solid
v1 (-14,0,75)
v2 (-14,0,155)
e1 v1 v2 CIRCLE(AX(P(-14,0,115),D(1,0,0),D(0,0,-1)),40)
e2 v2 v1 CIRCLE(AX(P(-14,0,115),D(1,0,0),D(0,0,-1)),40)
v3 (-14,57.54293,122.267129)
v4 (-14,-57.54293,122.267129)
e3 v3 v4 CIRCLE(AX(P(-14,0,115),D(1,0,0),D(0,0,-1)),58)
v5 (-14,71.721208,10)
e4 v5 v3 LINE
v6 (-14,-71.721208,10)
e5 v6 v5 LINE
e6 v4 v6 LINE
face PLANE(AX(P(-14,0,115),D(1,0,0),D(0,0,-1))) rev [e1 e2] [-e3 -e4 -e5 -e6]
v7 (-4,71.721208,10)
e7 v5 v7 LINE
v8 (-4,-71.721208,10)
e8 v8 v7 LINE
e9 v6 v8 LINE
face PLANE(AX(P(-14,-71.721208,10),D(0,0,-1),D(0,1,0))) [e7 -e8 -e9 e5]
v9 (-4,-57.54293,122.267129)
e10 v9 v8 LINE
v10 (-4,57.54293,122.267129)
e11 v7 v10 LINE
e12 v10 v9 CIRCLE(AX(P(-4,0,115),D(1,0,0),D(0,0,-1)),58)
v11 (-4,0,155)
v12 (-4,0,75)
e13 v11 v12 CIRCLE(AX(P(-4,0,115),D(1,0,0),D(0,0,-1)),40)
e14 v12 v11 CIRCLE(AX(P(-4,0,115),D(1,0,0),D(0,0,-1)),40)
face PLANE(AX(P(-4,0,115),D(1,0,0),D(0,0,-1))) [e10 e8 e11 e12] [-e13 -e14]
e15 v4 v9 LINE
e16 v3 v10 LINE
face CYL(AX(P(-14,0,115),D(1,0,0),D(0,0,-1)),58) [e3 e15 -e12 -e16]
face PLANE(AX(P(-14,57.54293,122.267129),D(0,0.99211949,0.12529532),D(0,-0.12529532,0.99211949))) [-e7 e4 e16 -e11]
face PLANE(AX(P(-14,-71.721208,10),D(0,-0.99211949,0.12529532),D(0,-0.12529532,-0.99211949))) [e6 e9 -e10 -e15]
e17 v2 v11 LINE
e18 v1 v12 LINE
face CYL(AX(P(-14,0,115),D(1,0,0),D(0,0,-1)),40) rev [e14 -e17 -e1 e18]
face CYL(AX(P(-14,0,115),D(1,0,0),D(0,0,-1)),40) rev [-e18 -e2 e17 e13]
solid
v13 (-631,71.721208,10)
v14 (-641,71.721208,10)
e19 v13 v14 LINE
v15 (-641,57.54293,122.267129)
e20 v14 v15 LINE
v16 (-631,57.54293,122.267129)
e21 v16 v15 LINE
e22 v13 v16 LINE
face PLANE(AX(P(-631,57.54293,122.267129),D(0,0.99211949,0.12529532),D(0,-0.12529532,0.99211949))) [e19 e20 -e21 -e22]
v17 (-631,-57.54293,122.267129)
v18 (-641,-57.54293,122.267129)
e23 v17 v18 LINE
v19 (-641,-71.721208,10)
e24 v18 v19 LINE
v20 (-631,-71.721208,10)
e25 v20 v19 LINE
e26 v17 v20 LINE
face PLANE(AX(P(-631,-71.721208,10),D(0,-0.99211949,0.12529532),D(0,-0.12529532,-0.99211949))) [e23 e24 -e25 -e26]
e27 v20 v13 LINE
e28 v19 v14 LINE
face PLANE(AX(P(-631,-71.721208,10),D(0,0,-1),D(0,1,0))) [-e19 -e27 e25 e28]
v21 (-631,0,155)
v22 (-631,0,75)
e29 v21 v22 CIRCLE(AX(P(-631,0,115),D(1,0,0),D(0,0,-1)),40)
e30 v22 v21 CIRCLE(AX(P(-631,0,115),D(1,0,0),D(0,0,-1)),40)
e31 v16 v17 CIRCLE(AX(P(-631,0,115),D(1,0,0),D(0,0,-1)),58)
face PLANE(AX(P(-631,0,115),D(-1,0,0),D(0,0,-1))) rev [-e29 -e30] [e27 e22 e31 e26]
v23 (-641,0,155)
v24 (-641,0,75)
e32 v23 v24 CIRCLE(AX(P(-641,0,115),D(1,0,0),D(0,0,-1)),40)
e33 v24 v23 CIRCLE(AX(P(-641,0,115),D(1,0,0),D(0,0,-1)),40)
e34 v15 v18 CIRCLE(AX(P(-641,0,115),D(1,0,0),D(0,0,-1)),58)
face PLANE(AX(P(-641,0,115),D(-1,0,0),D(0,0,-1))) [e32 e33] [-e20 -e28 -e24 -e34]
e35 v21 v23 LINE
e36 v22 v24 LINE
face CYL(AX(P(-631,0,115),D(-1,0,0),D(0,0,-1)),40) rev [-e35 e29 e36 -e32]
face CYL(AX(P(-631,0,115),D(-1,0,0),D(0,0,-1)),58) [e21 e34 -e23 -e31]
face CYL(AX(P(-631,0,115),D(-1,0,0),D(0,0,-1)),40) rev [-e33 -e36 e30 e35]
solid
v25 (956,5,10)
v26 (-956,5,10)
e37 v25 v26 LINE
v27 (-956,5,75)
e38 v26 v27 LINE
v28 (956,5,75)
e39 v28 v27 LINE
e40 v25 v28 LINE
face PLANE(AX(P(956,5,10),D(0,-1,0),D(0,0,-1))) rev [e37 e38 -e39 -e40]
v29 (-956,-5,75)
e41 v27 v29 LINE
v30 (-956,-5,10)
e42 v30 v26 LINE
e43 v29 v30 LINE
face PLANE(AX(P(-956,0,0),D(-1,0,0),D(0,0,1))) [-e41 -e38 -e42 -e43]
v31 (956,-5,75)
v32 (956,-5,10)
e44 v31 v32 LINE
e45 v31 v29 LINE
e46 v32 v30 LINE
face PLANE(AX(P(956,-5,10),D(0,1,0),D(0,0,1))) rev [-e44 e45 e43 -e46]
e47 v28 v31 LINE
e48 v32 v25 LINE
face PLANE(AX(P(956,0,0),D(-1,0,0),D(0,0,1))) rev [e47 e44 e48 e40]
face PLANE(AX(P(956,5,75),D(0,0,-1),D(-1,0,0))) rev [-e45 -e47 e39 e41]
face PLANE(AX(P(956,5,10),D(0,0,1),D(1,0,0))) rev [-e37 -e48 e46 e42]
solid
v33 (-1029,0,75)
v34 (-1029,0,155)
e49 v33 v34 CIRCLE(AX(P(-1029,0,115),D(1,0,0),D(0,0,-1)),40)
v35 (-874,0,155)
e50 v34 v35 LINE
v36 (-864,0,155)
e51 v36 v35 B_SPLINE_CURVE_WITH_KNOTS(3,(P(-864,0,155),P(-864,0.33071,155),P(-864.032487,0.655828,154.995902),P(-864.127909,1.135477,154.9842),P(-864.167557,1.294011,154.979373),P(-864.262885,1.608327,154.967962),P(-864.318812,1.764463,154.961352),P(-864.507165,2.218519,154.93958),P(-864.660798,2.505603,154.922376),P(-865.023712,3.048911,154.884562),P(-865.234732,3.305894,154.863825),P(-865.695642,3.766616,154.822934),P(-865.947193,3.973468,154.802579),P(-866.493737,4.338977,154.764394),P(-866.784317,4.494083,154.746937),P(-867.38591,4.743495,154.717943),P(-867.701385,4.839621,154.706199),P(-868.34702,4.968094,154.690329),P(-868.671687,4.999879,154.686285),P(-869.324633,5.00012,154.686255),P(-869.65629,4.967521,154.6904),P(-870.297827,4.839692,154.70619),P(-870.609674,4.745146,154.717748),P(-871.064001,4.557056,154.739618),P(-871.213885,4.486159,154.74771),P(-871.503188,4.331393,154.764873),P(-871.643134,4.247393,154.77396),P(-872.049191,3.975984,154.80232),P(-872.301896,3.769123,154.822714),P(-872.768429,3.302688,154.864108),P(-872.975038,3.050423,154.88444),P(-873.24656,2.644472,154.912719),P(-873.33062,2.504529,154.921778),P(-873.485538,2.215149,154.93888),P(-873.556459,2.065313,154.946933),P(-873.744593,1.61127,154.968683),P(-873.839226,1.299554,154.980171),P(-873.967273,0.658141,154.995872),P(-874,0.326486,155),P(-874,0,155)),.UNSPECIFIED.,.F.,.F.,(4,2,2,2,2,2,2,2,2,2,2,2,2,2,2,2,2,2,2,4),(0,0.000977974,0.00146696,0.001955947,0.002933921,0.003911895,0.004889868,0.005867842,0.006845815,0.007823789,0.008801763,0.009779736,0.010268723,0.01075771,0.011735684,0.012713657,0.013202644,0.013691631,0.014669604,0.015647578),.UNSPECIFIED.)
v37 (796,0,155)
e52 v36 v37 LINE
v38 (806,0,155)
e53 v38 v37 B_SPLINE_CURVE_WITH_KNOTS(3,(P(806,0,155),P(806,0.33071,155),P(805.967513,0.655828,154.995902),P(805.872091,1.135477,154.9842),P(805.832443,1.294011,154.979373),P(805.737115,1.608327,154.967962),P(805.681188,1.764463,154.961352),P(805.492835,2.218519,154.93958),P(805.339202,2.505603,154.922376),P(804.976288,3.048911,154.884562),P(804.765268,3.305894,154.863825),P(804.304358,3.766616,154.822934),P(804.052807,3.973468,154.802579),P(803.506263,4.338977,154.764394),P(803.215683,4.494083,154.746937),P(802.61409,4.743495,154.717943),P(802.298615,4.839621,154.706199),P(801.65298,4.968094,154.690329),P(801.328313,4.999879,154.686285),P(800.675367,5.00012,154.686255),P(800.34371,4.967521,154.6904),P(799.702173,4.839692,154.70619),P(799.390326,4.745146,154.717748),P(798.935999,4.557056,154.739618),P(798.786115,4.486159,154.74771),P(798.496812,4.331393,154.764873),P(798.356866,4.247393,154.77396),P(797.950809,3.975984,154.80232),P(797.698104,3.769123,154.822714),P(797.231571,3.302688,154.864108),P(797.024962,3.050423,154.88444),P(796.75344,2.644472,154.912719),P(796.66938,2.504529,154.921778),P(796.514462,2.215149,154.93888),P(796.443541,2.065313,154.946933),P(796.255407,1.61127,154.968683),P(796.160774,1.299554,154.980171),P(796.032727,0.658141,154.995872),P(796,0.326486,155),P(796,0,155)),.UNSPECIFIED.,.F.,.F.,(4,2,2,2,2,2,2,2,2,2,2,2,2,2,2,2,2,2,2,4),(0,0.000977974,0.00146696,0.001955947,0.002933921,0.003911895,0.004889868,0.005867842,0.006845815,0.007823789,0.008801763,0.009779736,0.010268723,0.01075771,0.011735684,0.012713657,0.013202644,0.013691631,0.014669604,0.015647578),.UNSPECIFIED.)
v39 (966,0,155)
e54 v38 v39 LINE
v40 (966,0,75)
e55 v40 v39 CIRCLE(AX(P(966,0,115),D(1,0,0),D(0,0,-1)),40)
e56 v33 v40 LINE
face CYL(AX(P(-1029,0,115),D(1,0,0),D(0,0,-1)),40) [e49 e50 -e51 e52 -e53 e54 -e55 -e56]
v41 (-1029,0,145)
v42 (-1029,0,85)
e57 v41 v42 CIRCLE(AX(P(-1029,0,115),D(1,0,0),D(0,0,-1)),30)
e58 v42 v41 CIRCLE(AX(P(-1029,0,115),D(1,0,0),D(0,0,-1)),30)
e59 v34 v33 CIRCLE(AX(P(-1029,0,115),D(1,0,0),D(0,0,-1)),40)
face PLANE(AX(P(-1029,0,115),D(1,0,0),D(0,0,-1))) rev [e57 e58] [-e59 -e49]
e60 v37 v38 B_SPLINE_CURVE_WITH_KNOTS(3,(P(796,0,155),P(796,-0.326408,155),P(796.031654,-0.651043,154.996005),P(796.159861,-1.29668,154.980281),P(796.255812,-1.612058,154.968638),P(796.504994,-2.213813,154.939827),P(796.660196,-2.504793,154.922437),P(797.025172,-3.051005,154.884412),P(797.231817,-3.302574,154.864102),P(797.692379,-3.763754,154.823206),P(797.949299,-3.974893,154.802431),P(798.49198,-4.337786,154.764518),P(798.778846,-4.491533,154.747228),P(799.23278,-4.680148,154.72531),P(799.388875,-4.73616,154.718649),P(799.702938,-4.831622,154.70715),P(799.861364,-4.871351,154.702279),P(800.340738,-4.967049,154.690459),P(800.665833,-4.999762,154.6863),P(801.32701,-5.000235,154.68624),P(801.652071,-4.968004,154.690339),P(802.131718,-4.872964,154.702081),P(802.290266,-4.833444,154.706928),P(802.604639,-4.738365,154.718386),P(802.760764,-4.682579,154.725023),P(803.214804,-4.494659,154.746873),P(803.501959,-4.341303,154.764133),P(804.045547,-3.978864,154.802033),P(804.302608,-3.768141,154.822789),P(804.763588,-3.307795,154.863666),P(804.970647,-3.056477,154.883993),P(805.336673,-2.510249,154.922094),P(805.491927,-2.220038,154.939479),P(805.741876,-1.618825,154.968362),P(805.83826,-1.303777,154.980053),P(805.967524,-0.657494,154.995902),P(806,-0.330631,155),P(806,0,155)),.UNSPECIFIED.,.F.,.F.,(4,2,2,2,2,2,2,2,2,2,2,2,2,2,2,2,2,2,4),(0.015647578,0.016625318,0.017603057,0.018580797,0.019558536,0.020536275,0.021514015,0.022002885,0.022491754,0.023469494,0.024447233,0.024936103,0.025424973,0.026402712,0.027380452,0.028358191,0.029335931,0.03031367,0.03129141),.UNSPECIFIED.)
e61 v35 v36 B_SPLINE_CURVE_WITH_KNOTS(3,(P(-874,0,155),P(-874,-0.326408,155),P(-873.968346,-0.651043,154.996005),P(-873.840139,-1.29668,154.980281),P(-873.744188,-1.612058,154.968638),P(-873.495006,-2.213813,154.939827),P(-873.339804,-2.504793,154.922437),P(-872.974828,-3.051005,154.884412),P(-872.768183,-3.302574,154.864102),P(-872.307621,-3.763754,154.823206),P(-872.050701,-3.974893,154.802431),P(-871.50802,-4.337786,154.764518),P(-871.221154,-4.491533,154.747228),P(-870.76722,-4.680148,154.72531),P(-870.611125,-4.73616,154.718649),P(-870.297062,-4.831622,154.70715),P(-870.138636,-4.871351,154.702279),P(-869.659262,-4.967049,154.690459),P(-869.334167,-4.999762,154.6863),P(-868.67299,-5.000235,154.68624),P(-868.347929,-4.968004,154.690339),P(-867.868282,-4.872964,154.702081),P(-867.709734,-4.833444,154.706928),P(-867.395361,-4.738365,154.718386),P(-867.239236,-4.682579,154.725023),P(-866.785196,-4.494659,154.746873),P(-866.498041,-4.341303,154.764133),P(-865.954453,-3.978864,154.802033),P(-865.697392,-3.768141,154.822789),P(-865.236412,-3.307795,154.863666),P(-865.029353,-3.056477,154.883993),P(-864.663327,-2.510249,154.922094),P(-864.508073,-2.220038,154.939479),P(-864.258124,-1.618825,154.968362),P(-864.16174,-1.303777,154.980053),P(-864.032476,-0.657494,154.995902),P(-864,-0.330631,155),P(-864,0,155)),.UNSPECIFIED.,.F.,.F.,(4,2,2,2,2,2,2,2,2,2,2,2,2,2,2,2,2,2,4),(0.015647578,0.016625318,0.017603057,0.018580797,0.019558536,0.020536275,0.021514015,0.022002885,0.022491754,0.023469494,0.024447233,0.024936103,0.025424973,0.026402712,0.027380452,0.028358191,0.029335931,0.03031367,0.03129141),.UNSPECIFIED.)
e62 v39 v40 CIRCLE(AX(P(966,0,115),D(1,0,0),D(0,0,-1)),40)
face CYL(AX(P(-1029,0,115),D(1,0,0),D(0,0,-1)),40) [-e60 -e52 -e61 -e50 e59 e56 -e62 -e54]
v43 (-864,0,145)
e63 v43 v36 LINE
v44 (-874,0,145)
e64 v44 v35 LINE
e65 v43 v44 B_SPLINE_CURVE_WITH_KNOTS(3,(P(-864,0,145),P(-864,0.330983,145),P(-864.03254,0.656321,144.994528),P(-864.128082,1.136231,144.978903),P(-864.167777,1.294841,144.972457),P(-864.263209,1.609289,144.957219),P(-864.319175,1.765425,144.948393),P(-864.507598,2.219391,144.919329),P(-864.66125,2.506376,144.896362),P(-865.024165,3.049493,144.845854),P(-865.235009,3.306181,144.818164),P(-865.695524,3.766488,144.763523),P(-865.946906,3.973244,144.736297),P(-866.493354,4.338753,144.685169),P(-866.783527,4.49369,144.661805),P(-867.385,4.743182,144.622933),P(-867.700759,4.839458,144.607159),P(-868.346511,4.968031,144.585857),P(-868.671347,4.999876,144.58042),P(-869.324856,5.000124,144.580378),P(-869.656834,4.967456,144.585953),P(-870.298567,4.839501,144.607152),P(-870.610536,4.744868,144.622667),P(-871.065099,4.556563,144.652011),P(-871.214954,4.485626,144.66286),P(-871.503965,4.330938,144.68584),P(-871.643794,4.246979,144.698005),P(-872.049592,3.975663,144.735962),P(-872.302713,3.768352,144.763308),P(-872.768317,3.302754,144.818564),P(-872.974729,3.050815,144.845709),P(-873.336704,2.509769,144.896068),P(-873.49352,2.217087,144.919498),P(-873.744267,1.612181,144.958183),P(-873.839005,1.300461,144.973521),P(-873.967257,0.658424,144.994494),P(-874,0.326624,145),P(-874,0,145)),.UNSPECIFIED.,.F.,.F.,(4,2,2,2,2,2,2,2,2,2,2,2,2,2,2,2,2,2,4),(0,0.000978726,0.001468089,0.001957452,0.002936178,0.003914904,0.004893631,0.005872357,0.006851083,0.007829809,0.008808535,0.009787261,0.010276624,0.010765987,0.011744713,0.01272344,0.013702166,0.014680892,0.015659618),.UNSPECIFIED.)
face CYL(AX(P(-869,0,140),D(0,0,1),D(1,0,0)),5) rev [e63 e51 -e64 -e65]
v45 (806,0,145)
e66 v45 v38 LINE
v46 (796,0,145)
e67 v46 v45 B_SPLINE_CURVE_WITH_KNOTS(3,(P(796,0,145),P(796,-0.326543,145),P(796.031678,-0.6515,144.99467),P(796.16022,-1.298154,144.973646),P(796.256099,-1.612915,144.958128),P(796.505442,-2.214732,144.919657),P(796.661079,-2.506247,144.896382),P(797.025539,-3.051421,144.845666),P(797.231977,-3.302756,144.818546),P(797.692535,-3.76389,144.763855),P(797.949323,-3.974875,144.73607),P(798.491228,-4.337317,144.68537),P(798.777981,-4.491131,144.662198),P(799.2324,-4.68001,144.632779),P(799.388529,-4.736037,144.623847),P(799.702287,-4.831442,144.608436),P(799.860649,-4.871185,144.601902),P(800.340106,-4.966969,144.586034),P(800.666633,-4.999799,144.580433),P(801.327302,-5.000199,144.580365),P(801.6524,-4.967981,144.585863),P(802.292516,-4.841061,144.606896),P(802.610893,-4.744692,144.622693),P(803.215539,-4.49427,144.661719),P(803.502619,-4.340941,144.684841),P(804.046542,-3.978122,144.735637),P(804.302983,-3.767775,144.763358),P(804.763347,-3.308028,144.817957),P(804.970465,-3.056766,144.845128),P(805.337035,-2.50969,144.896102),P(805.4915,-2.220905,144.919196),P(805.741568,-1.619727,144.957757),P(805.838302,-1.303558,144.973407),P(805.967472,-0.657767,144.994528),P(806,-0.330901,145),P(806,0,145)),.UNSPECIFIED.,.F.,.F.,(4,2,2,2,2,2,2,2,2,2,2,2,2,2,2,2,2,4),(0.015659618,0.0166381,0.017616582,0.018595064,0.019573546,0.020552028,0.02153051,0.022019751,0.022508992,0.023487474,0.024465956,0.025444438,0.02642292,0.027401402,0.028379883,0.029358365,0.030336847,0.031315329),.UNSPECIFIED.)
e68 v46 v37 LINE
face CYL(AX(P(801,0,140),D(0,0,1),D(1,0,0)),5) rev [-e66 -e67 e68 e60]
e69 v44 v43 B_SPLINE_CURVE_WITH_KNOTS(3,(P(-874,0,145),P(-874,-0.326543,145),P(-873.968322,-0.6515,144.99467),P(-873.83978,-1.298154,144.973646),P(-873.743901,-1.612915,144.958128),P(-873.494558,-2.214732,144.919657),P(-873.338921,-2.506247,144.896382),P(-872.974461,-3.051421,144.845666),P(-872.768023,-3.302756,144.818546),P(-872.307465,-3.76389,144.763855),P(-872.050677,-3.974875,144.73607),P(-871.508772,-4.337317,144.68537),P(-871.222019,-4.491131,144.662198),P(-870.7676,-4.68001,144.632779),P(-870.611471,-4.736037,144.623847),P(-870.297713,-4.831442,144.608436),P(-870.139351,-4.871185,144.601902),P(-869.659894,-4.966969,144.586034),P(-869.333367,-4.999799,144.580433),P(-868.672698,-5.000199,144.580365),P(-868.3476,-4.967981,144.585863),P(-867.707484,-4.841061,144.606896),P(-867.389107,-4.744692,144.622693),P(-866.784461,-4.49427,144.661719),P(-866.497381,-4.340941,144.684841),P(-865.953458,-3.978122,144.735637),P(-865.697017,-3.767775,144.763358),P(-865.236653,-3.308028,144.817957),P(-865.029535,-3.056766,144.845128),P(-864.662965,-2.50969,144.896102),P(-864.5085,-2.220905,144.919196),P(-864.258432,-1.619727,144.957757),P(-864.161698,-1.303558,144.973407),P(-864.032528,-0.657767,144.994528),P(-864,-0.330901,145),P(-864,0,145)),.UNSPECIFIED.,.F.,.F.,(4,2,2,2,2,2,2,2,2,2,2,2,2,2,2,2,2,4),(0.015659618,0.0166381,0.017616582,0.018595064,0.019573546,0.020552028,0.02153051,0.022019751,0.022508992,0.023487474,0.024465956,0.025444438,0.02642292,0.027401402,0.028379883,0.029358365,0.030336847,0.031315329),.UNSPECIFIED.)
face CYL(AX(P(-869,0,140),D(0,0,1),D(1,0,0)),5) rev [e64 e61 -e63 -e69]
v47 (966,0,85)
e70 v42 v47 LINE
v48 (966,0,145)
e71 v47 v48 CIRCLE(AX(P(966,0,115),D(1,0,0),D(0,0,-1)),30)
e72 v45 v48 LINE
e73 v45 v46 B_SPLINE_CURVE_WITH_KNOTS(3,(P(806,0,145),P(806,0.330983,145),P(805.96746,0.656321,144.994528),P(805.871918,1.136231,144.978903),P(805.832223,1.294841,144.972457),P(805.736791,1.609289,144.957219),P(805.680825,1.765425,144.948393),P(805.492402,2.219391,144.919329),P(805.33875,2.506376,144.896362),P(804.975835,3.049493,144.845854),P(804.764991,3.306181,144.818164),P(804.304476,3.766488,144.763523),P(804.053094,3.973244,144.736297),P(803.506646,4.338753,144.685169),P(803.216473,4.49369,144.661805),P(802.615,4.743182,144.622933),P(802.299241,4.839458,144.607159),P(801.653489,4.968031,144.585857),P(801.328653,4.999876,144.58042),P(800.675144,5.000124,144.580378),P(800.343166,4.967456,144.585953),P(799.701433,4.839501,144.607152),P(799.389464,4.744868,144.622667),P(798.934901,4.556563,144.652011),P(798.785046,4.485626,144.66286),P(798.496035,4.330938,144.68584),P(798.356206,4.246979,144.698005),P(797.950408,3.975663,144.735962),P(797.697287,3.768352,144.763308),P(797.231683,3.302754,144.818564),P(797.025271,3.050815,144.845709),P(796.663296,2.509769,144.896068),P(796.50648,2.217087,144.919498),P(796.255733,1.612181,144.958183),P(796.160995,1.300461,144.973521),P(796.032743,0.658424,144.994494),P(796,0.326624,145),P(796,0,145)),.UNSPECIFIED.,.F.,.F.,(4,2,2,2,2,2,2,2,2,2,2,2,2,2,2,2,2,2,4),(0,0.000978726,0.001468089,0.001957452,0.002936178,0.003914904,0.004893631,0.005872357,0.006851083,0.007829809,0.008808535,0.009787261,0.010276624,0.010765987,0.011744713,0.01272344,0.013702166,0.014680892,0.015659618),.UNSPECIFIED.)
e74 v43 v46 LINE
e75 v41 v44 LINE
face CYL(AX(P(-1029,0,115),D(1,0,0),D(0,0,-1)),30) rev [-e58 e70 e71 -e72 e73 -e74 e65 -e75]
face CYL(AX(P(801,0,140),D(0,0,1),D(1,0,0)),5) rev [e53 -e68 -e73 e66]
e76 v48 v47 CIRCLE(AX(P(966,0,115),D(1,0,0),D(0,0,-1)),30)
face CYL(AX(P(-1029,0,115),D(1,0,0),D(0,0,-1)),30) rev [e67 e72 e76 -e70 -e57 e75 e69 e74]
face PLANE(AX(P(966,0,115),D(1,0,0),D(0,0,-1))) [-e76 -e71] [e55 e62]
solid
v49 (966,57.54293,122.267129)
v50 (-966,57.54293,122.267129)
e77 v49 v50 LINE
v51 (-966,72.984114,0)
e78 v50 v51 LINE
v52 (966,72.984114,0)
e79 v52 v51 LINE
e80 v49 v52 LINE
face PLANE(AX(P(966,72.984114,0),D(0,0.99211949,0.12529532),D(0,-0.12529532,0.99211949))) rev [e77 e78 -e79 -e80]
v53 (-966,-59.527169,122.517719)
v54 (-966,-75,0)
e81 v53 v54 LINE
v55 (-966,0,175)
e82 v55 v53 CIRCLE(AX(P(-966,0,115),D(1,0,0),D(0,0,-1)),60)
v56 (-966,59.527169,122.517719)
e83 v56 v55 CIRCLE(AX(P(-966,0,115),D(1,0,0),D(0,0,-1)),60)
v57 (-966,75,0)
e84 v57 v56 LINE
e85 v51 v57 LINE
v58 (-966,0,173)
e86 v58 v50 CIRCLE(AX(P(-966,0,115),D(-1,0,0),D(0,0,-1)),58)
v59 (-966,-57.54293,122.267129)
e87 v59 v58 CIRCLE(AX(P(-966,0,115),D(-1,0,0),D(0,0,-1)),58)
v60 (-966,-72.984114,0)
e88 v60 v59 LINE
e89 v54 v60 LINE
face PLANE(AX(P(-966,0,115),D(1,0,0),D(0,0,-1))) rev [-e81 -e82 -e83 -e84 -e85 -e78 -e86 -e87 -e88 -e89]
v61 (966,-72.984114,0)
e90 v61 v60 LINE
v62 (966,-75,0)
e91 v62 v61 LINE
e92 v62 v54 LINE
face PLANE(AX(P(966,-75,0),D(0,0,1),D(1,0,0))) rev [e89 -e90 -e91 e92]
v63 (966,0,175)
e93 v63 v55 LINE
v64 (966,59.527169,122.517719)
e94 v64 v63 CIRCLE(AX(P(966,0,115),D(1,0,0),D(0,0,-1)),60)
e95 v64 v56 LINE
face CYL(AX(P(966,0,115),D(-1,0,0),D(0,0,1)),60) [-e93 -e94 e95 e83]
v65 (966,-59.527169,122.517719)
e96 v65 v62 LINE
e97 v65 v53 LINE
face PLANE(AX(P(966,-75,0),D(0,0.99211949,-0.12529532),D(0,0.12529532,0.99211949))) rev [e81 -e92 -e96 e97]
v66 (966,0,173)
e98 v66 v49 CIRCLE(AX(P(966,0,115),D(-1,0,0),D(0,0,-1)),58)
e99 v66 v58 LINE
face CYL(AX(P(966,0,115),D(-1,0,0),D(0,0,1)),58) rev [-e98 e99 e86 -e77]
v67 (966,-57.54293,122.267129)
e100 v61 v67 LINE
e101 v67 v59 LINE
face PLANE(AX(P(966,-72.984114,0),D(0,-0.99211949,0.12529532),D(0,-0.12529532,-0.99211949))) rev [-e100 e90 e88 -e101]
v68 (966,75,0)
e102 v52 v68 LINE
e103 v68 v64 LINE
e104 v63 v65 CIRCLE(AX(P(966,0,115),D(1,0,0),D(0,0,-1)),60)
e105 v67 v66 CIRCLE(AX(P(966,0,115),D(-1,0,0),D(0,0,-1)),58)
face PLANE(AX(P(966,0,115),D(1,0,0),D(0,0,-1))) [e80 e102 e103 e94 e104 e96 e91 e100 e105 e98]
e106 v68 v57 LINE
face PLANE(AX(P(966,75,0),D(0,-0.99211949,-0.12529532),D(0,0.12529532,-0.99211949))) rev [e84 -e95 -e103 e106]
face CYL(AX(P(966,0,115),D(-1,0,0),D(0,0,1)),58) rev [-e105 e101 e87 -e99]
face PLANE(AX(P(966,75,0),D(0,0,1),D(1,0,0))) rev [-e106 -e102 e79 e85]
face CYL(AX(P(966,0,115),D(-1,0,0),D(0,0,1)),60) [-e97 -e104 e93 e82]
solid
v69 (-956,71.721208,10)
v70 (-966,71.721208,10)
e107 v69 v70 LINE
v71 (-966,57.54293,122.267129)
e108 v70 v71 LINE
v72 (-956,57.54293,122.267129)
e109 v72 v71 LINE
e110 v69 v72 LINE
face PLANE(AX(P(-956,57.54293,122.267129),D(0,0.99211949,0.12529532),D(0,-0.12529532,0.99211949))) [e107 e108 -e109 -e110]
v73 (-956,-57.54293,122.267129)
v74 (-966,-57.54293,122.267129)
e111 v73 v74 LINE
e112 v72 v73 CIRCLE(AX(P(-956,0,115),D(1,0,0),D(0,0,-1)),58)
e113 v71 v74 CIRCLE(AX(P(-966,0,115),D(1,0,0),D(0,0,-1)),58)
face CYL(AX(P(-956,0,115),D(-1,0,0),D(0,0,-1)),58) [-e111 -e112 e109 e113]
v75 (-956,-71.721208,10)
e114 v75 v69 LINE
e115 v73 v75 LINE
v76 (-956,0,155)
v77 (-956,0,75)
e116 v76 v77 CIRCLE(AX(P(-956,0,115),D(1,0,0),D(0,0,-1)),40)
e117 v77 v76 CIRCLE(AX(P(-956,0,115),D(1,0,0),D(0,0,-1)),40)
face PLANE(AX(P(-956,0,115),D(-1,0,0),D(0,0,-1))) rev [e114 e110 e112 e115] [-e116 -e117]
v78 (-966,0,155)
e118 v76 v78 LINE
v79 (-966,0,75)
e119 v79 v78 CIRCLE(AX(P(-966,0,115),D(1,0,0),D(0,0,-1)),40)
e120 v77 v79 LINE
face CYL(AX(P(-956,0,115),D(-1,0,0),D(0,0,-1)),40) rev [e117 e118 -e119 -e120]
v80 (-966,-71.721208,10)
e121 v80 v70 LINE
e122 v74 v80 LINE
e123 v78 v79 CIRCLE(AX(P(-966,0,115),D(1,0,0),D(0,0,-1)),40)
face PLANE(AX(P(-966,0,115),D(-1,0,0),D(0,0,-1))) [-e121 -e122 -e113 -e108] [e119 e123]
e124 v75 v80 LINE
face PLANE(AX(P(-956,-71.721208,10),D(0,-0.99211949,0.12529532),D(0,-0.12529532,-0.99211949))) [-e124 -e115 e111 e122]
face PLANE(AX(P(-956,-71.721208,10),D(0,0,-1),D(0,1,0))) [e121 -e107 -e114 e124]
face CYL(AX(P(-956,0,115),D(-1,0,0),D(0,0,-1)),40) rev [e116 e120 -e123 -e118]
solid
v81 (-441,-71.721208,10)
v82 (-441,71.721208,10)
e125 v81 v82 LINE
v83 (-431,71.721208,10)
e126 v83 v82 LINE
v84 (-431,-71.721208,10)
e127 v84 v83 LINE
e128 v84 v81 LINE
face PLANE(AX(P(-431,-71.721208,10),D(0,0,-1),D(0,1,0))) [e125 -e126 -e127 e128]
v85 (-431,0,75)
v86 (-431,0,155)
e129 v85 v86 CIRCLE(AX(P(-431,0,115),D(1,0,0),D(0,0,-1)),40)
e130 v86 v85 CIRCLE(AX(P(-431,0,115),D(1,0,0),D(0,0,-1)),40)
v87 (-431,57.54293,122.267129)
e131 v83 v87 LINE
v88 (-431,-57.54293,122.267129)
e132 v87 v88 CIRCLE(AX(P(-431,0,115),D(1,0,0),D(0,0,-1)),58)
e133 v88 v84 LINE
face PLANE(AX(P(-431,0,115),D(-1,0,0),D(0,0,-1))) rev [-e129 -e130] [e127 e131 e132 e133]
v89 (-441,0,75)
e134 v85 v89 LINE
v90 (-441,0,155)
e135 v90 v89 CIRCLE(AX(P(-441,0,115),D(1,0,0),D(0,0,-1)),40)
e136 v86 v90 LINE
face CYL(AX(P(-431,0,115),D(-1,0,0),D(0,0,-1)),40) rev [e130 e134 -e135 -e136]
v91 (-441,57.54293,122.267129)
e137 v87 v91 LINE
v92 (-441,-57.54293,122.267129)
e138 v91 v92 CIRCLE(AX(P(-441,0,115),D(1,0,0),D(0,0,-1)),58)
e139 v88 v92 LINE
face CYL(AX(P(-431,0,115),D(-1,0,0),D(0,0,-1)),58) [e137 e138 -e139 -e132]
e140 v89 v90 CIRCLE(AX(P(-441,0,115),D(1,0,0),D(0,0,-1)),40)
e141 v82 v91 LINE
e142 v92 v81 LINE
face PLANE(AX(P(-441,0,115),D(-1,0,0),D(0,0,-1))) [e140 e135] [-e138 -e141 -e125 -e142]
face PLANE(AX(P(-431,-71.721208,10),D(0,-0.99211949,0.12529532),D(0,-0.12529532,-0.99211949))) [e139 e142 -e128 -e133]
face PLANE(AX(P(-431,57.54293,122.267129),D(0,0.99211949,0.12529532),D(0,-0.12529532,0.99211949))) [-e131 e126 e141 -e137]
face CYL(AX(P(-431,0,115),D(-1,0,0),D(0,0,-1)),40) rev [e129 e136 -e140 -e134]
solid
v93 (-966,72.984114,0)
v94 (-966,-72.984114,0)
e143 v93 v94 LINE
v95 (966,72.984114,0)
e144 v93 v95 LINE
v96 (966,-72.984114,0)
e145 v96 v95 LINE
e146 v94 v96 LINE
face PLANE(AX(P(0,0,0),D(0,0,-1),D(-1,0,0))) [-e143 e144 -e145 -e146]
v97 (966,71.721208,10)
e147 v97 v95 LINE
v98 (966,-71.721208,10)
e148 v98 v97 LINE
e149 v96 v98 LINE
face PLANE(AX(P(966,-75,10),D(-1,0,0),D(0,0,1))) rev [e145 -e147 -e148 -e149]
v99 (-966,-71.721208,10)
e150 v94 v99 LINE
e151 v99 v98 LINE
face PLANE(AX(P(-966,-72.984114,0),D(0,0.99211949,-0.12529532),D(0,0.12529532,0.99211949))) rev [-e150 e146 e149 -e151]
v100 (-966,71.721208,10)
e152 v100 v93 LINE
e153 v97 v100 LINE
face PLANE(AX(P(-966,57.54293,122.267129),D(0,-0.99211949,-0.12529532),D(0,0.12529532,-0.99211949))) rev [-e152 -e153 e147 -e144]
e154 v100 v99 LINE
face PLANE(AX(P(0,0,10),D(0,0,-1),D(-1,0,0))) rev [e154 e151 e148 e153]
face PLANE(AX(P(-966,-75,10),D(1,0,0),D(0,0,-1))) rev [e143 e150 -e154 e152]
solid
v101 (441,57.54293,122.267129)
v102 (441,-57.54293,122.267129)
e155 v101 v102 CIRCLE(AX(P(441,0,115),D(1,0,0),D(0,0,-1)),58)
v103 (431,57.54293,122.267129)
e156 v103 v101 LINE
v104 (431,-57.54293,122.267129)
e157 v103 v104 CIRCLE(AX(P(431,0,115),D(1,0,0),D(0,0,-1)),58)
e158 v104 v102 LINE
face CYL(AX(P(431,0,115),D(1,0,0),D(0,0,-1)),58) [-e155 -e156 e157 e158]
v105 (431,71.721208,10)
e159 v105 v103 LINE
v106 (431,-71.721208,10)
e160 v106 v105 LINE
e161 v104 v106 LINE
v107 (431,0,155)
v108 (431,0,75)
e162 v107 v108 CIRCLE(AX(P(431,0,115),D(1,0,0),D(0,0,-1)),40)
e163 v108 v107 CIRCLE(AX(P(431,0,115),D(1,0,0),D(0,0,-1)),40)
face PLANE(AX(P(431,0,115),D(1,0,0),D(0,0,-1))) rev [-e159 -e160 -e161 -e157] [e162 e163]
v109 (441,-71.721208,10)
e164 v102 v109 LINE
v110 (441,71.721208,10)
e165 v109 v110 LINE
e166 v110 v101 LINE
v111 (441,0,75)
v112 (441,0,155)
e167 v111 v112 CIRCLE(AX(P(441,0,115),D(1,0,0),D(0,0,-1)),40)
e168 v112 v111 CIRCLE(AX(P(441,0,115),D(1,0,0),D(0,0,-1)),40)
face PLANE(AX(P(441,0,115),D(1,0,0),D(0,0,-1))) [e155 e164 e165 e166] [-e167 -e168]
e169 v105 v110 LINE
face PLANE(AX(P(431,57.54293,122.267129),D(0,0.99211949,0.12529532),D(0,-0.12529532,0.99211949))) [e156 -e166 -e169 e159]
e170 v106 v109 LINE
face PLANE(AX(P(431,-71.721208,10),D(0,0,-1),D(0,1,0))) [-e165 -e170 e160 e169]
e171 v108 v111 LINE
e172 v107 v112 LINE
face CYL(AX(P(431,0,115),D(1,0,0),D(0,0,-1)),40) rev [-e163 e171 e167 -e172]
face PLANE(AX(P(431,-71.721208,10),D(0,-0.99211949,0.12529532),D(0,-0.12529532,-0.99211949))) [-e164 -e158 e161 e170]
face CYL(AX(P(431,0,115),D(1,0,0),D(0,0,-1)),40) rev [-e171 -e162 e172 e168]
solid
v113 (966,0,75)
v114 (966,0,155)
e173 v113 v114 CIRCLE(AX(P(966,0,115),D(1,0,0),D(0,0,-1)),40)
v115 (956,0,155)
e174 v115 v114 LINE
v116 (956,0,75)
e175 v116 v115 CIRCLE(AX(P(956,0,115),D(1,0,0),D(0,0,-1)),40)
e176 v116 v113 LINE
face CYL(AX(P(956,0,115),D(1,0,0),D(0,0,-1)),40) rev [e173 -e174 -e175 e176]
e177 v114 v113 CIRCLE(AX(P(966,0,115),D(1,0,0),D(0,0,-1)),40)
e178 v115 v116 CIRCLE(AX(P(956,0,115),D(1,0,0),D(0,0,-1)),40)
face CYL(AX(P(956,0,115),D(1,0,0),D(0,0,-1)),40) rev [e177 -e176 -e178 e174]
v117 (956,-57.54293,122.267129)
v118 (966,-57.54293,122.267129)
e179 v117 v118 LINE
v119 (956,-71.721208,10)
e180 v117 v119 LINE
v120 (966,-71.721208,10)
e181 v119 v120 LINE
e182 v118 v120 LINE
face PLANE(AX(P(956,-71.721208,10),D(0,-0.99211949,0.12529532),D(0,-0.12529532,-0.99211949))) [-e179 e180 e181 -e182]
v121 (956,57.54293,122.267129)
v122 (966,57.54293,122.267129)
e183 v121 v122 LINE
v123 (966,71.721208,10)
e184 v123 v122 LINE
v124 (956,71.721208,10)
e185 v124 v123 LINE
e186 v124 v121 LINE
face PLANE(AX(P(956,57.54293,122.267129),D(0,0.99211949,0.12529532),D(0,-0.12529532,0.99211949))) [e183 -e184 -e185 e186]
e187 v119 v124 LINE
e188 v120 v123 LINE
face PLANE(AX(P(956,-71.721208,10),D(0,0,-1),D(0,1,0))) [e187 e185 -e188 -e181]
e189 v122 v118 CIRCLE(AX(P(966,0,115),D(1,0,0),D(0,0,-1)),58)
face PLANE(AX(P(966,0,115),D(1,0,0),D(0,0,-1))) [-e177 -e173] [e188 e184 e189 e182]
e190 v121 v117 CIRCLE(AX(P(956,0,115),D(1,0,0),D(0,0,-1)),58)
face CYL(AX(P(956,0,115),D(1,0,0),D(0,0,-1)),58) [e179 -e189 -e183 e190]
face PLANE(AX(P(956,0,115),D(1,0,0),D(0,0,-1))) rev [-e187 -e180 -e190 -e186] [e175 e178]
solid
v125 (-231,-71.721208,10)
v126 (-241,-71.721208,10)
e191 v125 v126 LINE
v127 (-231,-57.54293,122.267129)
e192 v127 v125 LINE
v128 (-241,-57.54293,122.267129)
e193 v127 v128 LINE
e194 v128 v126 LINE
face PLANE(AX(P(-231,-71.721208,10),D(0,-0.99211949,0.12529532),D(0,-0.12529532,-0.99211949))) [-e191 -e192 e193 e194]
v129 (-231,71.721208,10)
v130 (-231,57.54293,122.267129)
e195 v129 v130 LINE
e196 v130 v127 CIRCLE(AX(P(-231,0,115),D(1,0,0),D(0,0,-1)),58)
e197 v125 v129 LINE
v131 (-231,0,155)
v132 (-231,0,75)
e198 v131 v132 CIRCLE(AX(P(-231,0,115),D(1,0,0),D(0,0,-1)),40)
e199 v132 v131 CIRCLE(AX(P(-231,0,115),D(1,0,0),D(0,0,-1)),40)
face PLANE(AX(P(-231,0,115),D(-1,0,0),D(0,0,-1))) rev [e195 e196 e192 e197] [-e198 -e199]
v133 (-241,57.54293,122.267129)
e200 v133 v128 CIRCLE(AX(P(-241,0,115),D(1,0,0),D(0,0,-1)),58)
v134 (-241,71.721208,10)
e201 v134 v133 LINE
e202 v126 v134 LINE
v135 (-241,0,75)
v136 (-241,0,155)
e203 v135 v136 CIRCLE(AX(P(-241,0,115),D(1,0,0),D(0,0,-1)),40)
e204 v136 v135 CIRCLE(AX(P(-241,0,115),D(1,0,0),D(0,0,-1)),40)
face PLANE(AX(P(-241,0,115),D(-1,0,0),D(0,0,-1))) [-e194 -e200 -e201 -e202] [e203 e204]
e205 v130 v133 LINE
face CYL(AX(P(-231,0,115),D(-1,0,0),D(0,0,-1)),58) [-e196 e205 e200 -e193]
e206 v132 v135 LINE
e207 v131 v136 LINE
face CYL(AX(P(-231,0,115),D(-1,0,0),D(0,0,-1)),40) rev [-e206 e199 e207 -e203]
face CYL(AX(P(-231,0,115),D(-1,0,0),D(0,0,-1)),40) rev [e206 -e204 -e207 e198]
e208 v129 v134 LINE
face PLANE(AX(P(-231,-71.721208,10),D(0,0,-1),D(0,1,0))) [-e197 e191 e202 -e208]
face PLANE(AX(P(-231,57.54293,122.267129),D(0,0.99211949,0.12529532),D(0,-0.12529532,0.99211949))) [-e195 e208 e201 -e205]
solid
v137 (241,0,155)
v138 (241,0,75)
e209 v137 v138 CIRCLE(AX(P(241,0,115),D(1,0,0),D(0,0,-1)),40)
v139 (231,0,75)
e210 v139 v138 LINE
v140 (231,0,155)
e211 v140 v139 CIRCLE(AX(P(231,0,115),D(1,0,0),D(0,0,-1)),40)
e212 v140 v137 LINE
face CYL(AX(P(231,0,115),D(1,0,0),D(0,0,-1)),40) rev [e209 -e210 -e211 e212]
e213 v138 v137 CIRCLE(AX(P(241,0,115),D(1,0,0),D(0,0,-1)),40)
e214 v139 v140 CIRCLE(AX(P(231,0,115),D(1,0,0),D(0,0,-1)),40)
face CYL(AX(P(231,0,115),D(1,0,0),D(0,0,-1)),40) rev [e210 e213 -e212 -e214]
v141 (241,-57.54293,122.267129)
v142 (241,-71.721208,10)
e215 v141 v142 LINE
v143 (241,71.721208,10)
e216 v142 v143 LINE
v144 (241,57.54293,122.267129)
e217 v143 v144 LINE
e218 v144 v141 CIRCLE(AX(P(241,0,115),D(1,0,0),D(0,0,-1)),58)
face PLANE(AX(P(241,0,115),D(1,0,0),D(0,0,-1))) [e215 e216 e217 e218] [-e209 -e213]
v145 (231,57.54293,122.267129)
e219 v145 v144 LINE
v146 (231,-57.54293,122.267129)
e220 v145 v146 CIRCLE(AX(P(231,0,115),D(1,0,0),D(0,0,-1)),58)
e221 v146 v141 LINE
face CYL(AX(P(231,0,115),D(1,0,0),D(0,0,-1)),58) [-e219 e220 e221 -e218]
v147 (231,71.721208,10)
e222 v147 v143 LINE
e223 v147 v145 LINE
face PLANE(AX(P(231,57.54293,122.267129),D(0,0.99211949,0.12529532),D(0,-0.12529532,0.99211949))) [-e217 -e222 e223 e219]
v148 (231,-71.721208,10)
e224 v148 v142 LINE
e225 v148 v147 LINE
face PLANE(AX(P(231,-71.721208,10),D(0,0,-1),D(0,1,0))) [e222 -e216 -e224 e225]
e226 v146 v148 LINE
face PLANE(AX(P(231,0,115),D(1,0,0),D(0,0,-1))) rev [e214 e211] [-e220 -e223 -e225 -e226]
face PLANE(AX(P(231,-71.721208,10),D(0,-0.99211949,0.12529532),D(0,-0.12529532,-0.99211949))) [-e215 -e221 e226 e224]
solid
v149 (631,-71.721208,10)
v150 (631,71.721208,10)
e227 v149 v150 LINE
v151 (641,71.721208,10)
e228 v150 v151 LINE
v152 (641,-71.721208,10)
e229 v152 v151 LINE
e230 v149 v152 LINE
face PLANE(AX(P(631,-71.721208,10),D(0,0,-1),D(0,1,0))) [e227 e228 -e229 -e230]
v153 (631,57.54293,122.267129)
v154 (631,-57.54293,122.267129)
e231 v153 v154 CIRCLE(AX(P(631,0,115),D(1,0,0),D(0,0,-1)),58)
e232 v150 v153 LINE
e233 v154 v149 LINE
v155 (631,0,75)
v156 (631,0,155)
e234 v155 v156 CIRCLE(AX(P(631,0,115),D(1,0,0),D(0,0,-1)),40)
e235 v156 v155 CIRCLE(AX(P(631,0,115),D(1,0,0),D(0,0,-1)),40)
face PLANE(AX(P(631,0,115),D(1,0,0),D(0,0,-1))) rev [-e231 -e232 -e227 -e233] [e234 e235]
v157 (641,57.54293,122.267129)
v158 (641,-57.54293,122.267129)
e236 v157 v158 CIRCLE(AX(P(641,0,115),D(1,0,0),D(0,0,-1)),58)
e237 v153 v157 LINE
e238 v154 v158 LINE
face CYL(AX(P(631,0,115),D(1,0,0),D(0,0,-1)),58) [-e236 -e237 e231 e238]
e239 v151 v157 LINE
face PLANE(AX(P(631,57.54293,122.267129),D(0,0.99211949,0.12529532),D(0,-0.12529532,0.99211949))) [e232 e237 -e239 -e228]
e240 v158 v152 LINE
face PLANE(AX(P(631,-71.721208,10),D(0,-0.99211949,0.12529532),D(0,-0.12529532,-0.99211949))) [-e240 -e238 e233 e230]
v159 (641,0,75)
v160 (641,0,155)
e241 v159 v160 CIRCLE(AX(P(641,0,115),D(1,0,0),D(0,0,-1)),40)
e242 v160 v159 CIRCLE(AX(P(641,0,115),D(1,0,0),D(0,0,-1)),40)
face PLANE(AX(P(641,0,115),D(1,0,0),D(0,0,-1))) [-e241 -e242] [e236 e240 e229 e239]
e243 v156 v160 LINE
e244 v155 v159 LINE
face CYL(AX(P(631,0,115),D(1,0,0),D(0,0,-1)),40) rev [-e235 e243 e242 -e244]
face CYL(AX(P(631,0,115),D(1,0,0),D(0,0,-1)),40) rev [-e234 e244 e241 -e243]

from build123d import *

# Parameters (mm, degrees)
SKETCH_1_W               = 1932
SKETCH_1_H               = 150
EXTRUDE_1_DEPTH          = 10
EXTRUDE_2_DEPTH          = 966
CUT_EXTRUDE_1_DEPTH      = 985.584176188
CUT_EXTRUDE_1_DEPTH_BACK = 985.584176188
SKETCH_4_R               = 40
EXTRUDE_3_DEPTH          = 10
PATTERN_LINEAR_1_COUNT   = 2
PATTERN_LINEAR_1_PITCH   = 325
PATTERN_LINEAR_2_COUNT   = 3
PATTERN_LINEAR_2_PITCH   = 200
PATTERN_LINEAR_3_COUNT   = 2
PATTERN_LINEAR_3_PITCH   = 245
SKETCH_5_R               = 40
SKETCH_5_R_2             = 30
EXTRUDE_4_DEPTH          = 1995
SKETCH_6_R               = 5
CUT_EXTRUDE_5_DEPTH      = 15
SKETCH_7_W               = 65
SKETCH_7_H               = 10
EXTRUDE_5_DEPTH          = 956


with BuildPart() as part:
    # 草图1 → 凸台-拉伸1 (new body)
    with BuildSketch(Plane.XY):
        Rectangle(SKETCH_1_W, SKETCH_1_H)
    extrude(amount=EXTRUDE_1_DEPTH)

    # 草图3 → 切除-拉伸1 (cut, two sides: drawn at the far end of the back side and taken through both)
    with BuildSketch(Plane(origin=(0, 0, 0), x_dir=(0, 0, -1), z_dir=(1, 0, 0)).offset(-CUT_EXTRUDE_1_DEPTH_BACK)):
        with BuildLine():
            Line((0, -72.984113789), (-122.267128543, -57.542930432))
            ThreePointArc((-122.267128543, -57.542930432), (-173, 0), (-122.267128543, 57.542930432))
            Line((-122.267128543, 57.542930432), (0, 72.984113789))
            Line((0, 72.984113789), (0, 76.636088329))
            Line((0, 76.636088329), (-197.071610704, 76.636088329))
            Line((-197.071610704, 76.636088329), (-197.071610704, -75))
            Line((-197.071610704, -75), (0, -75))
            Line((0, -75), (0, -72.984113789))
        make_face()
    extrude(amount=CUT_EXTRUDE_1_DEPTH + CUT_EXTRUDE_1_DEPTH_BACK, mode=Mode.SUBTRACT)


with BuildPart() as body_2:
    # 草图2 → 凸台-拉伸2 (new, symmetric)
    with BuildSketch(Plane(origin=(0, 0, 0), x_dir=(0, 0, -1), z_dir=(1, 0, 0))):
        with BuildLine():
            Line((0, 75), (-122.517719182, 59.527169413))
            ThreePointArc((-122.517719182, 59.527169413), (-175, 0), (-122.517719182, -59.527169413))
            Line((-122.517719182, -59.527169413), (0, -75))
            Line((0, -75), (0, -72.984113789))
            Line((0, -72.984113789), (-122.267128543, -57.542930432))
            ThreePointArc((-122.267128543, -57.542930432), (-173, 0), (-122.267128543, 57.542930432))
            Line((-122.267128543, 57.542930432), (0, 72.984113789))
            Line((0, 72.984113789), (0, 75))
        make_face()
    extrude(amount=EXTRUDE_2_DEPTH, both=True)


with BuildPart() as body_3:
    # 草图4 → 凸台-拉伸3 (new body)
    with BuildSketch(Plane(origin=(966, 0, 0), x_dir=(0, 0, -1), z_dir=(1, 0, 0))):
        with BuildLine():
            Line((-10, -71.721208253), (-122.267128543, -57.542930432))
            ThreePointArc((-122.267128543, -57.542930432), (-173, 0), (-122.267128543, 57.542930432))
            Line((-122.267128543, 57.542930432), (-10, 71.721208253))
            Line((-10, 71.721208253), (-10, -71.721208253))
        make_face()
        with Locations((-115, 0)):
            Circle(SKETCH_4_R, mode=Mode.SUBTRACT)
    extrude(amount=-EXTRUDE_3_DEPTH)


with BuildPart() as pattern_linear_1_1:
    # 阵列(线性)1: pattern copy
    add(body_3.part.moved(Location(Vector(-1, 0, 0) * (1 * PATTERN_LINEAR_1_PITCH))))


with BuildPart() as pattern_linear_2_1:
    # 阵列(线性)2: pattern copy
    add(pattern_linear_1_1.part.moved(Location(Vector(-1, 0, 0) * (1 * PATTERN_LINEAR_2_PITCH))))


with BuildPart() as pattern_linear_2_2:
    # 阵列(线性)2: pattern copy
    add(pattern_linear_1_1.part.moved(Location(Vector(-1, 0, 0) * (2 * PATTERN_LINEAR_2_PITCH))))


with BuildPart() as pattern_linear_3_1:
    # 阵列(线性)3: pattern copy
    add(pattern_linear_2_2.part.moved(Location(Vector(-1, 0, 0) * (1 * PATTERN_LINEAR_3_PITCH))))


with BuildPart() as body_8:
    # 镜向1: mirrored copy
    add(body_3.part.mirror(Plane(origin=(0, 0, 0), x_dir=(0, 0, 1), z_dir=(1, 0, 0))))


with BuildPart() as body_9:
    # Mirror 1 2: mirrored copy
    add(pattern_linear_2_2.part.mirror(Plane(origin=(0, 0, 0), x_dir=(0, 0, 1), z_dir=(1, 0, 0))))


with BuildPart() as body_10:
    # Mirror 1 3: mirrored copy
    add(pattern_linear_2_1.part.mirror(Plane(origin=(0, 0, 0), x_dir=(0, 0, 1), z_dir=(1, 0, 0))))


with BuildPart() as body_11:
    # Mirror 1 4: mirrored copy
    add(pattern_linear_1_1.part.mirror(Plane(origin=(0, 0, 0), x_dir=(0, 0, 1), z_dir=(1, 0, 0))))


with BuildPart() as body_12:
    # 草图5 → 凸台-拉伸4 (new body)
    with BuildSketch(Plane(origin=(966, 0, 0), x_dir=(0, 0, -1), z_dir=(1, 0, 0))):
        with Locations((-115, 0)):
            Circle(SKETCH_5_R)
        with Locations((-115, 0)):
            Circle(SKETCH_5_R_2, mode=Mode.SUBTRACT)
    extrude(amount=-EXTRUDE_4_DEPTH)

    # 草图6 → 切除-拉伸5 (cut, symmetric)
    with BuildSketch(Plane.XY.offset(155)):
        with Locations((801, 0)):
            Circle(SKETCH_6_R)
        with Locations((-869, 0)):
            Circle(SKETCH_6_R)
    extrude(amount=CUT_EXTRUDE_5_DEPTH, both=True, mode=Mode.SUBTRACT)


with BuildPart() as body_13:
    # 草图7 → 凸台-拉伸5 (new, symmetric)
    with BuildSketch(Plane(origin=(0, 0, 0), x_dir=(0, 0, -1), z_dir=(1, 0, 0))):
        with Locations((-42.5, 0)):
            Rectangle(SKETCH_7_W, SKETCH_7_H)
    extrude(amount=EXTRUDE_5_DEPTH, both=True)


solid = Compound([part.part, body_2.part, body_3.part, pattern_linear_1_1.part, pattern_linear_2_1.part, pattern_linear_2_2.part, pattern_linear_3_1.part, body_8.part, body_9.part, body_10.part, body_11.part, body_12.part, body_13.part])
